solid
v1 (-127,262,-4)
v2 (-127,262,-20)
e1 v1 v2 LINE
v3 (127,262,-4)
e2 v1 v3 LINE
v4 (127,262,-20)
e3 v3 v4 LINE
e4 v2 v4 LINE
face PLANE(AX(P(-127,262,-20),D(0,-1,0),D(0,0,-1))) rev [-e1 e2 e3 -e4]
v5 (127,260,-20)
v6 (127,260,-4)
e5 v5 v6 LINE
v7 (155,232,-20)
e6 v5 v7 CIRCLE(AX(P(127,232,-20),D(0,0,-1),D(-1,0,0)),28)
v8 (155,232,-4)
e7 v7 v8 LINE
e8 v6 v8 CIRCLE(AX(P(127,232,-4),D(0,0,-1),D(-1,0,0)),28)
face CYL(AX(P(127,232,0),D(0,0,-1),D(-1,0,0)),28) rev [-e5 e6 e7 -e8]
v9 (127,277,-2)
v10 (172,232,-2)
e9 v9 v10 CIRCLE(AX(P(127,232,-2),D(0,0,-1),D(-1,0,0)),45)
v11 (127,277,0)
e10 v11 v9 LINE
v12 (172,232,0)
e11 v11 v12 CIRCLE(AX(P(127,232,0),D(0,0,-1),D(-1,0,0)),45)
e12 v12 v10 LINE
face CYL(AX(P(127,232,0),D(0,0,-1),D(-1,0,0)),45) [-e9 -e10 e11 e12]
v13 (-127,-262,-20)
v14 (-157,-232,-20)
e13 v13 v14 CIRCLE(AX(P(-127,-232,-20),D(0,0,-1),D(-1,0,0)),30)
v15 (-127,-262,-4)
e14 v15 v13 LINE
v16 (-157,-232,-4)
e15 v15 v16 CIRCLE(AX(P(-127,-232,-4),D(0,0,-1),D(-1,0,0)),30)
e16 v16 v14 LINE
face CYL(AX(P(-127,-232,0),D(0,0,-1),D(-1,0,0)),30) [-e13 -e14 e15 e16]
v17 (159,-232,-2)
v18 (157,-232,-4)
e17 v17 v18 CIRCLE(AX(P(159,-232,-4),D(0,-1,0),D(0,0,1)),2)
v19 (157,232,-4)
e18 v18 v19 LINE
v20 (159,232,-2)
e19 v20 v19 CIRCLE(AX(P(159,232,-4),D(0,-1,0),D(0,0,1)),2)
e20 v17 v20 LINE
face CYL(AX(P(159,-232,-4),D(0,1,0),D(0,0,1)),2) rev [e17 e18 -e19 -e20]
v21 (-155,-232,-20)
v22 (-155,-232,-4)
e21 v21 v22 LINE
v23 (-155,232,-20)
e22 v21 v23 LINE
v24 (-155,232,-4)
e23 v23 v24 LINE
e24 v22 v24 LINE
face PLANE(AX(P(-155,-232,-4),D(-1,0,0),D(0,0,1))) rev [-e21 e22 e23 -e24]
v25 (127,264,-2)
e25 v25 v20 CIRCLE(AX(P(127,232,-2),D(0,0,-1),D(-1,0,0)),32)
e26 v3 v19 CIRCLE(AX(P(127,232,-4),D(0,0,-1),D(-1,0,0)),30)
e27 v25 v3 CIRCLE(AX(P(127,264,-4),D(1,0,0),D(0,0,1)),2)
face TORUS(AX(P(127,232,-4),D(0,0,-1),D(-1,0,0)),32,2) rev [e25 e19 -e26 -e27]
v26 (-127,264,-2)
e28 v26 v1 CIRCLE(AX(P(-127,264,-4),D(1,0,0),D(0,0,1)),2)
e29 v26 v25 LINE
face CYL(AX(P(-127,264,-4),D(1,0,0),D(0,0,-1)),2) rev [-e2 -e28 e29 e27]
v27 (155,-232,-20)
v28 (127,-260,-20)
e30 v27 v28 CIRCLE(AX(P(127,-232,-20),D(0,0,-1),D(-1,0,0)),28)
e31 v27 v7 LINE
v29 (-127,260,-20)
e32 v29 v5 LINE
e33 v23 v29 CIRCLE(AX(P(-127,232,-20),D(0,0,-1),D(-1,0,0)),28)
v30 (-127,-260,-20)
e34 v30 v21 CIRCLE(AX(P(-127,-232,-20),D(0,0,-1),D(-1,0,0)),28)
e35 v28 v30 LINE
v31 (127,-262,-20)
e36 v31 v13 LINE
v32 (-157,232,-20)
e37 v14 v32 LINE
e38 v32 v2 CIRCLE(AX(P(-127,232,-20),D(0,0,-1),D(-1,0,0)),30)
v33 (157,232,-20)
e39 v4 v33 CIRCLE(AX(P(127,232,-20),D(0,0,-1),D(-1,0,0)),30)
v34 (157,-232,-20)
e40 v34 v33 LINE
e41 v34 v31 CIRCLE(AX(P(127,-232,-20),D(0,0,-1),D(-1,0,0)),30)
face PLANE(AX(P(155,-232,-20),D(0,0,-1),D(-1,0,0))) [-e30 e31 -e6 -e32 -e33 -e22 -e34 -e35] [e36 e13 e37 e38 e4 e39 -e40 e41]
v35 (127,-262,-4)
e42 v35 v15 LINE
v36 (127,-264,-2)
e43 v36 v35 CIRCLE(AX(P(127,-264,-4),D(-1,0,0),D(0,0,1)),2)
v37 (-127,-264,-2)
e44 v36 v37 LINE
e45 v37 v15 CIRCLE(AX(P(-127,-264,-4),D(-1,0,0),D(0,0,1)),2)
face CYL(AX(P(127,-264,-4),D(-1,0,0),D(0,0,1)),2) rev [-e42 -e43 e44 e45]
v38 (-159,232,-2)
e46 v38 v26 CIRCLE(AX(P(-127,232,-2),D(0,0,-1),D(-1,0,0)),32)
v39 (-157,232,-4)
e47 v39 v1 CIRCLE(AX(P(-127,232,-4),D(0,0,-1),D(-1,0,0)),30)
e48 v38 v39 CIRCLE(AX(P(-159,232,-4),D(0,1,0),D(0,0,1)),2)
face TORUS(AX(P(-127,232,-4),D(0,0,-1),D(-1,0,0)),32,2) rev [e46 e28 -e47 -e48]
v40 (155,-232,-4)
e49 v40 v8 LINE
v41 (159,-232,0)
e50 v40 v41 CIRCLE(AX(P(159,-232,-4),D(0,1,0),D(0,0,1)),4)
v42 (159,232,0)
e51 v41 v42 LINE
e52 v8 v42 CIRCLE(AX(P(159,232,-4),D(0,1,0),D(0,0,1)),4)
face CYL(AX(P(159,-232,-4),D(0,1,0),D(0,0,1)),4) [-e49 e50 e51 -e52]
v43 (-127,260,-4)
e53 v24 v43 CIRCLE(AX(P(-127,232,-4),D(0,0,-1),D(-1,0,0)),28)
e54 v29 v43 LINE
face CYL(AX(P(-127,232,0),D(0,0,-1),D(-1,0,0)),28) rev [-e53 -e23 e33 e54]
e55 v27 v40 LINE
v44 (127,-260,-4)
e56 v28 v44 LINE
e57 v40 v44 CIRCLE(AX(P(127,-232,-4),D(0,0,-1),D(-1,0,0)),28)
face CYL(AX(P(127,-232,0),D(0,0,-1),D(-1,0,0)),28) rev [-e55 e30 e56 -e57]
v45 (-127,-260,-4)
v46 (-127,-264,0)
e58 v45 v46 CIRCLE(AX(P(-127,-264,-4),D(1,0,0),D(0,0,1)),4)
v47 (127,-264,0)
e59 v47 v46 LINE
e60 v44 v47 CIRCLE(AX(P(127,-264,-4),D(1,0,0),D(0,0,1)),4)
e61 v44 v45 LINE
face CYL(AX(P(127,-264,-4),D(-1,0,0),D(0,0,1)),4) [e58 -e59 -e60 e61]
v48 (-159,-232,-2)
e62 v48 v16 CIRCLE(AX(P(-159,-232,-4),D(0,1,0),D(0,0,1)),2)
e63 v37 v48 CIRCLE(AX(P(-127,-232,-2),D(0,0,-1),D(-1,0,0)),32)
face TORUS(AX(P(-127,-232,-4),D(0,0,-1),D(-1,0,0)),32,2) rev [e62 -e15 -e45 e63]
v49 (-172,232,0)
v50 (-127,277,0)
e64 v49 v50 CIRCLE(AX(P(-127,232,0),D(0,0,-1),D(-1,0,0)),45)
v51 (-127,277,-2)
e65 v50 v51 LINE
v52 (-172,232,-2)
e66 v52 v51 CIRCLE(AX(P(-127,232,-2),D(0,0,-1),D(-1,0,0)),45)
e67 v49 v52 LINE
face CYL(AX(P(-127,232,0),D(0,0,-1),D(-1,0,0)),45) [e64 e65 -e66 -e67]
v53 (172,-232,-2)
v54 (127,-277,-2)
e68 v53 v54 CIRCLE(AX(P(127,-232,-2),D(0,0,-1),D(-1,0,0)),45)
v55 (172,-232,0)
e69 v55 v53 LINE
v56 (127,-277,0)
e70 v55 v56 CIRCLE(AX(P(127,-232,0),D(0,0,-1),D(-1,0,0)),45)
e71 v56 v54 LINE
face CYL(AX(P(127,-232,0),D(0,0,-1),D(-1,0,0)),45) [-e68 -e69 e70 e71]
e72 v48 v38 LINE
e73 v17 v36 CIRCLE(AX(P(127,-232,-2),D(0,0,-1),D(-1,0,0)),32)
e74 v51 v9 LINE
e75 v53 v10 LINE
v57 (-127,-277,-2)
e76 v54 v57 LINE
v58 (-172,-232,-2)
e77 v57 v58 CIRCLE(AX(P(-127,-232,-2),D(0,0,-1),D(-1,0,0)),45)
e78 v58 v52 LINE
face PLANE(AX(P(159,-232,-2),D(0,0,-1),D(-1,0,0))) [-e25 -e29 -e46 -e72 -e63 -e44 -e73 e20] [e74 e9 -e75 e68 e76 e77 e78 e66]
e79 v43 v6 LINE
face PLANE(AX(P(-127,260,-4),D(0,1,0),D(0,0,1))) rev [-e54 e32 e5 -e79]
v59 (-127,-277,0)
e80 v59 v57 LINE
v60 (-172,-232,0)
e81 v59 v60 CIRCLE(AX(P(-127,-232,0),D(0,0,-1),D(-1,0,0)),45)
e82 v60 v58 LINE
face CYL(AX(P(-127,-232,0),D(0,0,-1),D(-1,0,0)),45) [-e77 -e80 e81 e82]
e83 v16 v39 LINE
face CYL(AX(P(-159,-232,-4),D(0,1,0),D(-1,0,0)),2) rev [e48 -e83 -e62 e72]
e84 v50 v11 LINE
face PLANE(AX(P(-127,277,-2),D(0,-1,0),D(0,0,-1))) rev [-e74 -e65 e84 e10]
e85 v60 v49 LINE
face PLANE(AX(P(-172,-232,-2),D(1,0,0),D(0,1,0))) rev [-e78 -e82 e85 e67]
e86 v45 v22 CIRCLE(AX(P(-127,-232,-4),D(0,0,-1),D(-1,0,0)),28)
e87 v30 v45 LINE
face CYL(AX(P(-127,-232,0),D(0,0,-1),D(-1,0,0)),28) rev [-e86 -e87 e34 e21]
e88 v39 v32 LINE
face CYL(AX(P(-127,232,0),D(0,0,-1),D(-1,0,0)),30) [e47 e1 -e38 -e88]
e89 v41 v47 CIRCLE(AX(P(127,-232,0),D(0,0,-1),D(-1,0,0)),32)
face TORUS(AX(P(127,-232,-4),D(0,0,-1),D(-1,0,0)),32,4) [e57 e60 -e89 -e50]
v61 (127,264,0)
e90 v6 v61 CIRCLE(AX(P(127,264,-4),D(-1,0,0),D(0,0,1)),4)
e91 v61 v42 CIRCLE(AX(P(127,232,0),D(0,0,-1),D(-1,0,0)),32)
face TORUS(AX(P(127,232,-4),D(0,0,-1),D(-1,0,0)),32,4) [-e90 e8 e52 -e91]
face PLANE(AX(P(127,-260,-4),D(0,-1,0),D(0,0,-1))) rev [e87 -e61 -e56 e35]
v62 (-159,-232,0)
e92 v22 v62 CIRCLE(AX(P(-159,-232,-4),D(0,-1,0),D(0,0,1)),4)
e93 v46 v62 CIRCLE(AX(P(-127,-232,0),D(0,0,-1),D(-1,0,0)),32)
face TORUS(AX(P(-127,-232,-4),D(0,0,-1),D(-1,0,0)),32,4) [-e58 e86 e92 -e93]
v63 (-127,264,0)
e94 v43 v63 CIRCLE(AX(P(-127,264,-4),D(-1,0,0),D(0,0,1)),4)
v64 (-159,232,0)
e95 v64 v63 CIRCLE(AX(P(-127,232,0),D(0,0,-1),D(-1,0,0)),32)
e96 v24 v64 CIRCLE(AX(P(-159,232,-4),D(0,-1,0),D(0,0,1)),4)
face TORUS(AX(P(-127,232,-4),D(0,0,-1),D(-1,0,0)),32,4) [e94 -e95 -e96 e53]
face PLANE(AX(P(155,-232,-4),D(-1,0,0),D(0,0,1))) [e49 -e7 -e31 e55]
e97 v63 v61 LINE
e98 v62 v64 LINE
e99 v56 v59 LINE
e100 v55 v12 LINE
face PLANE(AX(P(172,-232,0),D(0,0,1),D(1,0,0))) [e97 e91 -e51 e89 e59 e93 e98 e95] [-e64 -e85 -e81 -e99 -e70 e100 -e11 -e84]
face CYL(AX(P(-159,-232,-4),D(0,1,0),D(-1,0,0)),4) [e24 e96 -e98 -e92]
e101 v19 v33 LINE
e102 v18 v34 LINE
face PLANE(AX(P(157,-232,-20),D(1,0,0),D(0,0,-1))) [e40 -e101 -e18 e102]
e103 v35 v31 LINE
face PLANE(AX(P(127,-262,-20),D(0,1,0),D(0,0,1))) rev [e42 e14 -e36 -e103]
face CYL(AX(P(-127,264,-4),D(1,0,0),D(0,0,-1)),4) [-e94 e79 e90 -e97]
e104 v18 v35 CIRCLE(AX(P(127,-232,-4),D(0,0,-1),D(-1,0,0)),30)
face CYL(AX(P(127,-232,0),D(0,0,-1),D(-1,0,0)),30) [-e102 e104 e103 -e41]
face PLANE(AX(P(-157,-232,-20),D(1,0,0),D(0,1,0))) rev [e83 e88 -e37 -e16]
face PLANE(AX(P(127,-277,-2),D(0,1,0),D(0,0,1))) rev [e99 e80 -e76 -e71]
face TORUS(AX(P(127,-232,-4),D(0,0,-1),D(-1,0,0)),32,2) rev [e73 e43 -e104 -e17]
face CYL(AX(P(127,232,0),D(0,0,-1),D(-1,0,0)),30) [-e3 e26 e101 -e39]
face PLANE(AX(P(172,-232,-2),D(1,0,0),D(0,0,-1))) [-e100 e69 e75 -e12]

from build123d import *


with BuildPart() as part:
    # Sweep1: sweep along a path in Sketch1
    with BuildLine(Plane.XY) as sweep1_path:
        Line((-127, 260), (127, 260))
        ThreePointArc((127, 260), (146.798989873, 251.798989873), (155, 232))
        Line((155, 232), (155, -232))
        ThreePointArc((155, -232), (146.798989873, -251.798989873), (127, -260))
        Line((127, -260), (-127, -260))
        ThreePointArc((-127, -260), (-146.798989873, -251.798989873), (-155, -232))
        Line((-155, -232), (-155, 232))
        ThreePointArc((-155, 232), (-146.798989873, 251.798989873), (-127, 260))
    # Sketch2 → Sweep1 (sweep)
    with BuildSketch(Plane(origin=(0, 0, 0), x_dir=(1, 0, 0), z_dir=(0, 1, 0))):
        with BuildLine():
            Line((155, 4), (155, 20))
            Line((155, 20), (157, 20))
            Line((157, 20), (157, 4))
            ThreePointArc((157, 4), (157.585786438, 2.585786438), (159, 2))
            Line((159, 2), (172, 2))
            Line((172, 2), (172, 0))
            Line((172, 0), (159, 0))
            ThreePointArc((159, 0), (156.171572875, 1.171572875), (155, 4))
        make_face()
    sweep(path=sweep1_path.line)


solid = part.part
